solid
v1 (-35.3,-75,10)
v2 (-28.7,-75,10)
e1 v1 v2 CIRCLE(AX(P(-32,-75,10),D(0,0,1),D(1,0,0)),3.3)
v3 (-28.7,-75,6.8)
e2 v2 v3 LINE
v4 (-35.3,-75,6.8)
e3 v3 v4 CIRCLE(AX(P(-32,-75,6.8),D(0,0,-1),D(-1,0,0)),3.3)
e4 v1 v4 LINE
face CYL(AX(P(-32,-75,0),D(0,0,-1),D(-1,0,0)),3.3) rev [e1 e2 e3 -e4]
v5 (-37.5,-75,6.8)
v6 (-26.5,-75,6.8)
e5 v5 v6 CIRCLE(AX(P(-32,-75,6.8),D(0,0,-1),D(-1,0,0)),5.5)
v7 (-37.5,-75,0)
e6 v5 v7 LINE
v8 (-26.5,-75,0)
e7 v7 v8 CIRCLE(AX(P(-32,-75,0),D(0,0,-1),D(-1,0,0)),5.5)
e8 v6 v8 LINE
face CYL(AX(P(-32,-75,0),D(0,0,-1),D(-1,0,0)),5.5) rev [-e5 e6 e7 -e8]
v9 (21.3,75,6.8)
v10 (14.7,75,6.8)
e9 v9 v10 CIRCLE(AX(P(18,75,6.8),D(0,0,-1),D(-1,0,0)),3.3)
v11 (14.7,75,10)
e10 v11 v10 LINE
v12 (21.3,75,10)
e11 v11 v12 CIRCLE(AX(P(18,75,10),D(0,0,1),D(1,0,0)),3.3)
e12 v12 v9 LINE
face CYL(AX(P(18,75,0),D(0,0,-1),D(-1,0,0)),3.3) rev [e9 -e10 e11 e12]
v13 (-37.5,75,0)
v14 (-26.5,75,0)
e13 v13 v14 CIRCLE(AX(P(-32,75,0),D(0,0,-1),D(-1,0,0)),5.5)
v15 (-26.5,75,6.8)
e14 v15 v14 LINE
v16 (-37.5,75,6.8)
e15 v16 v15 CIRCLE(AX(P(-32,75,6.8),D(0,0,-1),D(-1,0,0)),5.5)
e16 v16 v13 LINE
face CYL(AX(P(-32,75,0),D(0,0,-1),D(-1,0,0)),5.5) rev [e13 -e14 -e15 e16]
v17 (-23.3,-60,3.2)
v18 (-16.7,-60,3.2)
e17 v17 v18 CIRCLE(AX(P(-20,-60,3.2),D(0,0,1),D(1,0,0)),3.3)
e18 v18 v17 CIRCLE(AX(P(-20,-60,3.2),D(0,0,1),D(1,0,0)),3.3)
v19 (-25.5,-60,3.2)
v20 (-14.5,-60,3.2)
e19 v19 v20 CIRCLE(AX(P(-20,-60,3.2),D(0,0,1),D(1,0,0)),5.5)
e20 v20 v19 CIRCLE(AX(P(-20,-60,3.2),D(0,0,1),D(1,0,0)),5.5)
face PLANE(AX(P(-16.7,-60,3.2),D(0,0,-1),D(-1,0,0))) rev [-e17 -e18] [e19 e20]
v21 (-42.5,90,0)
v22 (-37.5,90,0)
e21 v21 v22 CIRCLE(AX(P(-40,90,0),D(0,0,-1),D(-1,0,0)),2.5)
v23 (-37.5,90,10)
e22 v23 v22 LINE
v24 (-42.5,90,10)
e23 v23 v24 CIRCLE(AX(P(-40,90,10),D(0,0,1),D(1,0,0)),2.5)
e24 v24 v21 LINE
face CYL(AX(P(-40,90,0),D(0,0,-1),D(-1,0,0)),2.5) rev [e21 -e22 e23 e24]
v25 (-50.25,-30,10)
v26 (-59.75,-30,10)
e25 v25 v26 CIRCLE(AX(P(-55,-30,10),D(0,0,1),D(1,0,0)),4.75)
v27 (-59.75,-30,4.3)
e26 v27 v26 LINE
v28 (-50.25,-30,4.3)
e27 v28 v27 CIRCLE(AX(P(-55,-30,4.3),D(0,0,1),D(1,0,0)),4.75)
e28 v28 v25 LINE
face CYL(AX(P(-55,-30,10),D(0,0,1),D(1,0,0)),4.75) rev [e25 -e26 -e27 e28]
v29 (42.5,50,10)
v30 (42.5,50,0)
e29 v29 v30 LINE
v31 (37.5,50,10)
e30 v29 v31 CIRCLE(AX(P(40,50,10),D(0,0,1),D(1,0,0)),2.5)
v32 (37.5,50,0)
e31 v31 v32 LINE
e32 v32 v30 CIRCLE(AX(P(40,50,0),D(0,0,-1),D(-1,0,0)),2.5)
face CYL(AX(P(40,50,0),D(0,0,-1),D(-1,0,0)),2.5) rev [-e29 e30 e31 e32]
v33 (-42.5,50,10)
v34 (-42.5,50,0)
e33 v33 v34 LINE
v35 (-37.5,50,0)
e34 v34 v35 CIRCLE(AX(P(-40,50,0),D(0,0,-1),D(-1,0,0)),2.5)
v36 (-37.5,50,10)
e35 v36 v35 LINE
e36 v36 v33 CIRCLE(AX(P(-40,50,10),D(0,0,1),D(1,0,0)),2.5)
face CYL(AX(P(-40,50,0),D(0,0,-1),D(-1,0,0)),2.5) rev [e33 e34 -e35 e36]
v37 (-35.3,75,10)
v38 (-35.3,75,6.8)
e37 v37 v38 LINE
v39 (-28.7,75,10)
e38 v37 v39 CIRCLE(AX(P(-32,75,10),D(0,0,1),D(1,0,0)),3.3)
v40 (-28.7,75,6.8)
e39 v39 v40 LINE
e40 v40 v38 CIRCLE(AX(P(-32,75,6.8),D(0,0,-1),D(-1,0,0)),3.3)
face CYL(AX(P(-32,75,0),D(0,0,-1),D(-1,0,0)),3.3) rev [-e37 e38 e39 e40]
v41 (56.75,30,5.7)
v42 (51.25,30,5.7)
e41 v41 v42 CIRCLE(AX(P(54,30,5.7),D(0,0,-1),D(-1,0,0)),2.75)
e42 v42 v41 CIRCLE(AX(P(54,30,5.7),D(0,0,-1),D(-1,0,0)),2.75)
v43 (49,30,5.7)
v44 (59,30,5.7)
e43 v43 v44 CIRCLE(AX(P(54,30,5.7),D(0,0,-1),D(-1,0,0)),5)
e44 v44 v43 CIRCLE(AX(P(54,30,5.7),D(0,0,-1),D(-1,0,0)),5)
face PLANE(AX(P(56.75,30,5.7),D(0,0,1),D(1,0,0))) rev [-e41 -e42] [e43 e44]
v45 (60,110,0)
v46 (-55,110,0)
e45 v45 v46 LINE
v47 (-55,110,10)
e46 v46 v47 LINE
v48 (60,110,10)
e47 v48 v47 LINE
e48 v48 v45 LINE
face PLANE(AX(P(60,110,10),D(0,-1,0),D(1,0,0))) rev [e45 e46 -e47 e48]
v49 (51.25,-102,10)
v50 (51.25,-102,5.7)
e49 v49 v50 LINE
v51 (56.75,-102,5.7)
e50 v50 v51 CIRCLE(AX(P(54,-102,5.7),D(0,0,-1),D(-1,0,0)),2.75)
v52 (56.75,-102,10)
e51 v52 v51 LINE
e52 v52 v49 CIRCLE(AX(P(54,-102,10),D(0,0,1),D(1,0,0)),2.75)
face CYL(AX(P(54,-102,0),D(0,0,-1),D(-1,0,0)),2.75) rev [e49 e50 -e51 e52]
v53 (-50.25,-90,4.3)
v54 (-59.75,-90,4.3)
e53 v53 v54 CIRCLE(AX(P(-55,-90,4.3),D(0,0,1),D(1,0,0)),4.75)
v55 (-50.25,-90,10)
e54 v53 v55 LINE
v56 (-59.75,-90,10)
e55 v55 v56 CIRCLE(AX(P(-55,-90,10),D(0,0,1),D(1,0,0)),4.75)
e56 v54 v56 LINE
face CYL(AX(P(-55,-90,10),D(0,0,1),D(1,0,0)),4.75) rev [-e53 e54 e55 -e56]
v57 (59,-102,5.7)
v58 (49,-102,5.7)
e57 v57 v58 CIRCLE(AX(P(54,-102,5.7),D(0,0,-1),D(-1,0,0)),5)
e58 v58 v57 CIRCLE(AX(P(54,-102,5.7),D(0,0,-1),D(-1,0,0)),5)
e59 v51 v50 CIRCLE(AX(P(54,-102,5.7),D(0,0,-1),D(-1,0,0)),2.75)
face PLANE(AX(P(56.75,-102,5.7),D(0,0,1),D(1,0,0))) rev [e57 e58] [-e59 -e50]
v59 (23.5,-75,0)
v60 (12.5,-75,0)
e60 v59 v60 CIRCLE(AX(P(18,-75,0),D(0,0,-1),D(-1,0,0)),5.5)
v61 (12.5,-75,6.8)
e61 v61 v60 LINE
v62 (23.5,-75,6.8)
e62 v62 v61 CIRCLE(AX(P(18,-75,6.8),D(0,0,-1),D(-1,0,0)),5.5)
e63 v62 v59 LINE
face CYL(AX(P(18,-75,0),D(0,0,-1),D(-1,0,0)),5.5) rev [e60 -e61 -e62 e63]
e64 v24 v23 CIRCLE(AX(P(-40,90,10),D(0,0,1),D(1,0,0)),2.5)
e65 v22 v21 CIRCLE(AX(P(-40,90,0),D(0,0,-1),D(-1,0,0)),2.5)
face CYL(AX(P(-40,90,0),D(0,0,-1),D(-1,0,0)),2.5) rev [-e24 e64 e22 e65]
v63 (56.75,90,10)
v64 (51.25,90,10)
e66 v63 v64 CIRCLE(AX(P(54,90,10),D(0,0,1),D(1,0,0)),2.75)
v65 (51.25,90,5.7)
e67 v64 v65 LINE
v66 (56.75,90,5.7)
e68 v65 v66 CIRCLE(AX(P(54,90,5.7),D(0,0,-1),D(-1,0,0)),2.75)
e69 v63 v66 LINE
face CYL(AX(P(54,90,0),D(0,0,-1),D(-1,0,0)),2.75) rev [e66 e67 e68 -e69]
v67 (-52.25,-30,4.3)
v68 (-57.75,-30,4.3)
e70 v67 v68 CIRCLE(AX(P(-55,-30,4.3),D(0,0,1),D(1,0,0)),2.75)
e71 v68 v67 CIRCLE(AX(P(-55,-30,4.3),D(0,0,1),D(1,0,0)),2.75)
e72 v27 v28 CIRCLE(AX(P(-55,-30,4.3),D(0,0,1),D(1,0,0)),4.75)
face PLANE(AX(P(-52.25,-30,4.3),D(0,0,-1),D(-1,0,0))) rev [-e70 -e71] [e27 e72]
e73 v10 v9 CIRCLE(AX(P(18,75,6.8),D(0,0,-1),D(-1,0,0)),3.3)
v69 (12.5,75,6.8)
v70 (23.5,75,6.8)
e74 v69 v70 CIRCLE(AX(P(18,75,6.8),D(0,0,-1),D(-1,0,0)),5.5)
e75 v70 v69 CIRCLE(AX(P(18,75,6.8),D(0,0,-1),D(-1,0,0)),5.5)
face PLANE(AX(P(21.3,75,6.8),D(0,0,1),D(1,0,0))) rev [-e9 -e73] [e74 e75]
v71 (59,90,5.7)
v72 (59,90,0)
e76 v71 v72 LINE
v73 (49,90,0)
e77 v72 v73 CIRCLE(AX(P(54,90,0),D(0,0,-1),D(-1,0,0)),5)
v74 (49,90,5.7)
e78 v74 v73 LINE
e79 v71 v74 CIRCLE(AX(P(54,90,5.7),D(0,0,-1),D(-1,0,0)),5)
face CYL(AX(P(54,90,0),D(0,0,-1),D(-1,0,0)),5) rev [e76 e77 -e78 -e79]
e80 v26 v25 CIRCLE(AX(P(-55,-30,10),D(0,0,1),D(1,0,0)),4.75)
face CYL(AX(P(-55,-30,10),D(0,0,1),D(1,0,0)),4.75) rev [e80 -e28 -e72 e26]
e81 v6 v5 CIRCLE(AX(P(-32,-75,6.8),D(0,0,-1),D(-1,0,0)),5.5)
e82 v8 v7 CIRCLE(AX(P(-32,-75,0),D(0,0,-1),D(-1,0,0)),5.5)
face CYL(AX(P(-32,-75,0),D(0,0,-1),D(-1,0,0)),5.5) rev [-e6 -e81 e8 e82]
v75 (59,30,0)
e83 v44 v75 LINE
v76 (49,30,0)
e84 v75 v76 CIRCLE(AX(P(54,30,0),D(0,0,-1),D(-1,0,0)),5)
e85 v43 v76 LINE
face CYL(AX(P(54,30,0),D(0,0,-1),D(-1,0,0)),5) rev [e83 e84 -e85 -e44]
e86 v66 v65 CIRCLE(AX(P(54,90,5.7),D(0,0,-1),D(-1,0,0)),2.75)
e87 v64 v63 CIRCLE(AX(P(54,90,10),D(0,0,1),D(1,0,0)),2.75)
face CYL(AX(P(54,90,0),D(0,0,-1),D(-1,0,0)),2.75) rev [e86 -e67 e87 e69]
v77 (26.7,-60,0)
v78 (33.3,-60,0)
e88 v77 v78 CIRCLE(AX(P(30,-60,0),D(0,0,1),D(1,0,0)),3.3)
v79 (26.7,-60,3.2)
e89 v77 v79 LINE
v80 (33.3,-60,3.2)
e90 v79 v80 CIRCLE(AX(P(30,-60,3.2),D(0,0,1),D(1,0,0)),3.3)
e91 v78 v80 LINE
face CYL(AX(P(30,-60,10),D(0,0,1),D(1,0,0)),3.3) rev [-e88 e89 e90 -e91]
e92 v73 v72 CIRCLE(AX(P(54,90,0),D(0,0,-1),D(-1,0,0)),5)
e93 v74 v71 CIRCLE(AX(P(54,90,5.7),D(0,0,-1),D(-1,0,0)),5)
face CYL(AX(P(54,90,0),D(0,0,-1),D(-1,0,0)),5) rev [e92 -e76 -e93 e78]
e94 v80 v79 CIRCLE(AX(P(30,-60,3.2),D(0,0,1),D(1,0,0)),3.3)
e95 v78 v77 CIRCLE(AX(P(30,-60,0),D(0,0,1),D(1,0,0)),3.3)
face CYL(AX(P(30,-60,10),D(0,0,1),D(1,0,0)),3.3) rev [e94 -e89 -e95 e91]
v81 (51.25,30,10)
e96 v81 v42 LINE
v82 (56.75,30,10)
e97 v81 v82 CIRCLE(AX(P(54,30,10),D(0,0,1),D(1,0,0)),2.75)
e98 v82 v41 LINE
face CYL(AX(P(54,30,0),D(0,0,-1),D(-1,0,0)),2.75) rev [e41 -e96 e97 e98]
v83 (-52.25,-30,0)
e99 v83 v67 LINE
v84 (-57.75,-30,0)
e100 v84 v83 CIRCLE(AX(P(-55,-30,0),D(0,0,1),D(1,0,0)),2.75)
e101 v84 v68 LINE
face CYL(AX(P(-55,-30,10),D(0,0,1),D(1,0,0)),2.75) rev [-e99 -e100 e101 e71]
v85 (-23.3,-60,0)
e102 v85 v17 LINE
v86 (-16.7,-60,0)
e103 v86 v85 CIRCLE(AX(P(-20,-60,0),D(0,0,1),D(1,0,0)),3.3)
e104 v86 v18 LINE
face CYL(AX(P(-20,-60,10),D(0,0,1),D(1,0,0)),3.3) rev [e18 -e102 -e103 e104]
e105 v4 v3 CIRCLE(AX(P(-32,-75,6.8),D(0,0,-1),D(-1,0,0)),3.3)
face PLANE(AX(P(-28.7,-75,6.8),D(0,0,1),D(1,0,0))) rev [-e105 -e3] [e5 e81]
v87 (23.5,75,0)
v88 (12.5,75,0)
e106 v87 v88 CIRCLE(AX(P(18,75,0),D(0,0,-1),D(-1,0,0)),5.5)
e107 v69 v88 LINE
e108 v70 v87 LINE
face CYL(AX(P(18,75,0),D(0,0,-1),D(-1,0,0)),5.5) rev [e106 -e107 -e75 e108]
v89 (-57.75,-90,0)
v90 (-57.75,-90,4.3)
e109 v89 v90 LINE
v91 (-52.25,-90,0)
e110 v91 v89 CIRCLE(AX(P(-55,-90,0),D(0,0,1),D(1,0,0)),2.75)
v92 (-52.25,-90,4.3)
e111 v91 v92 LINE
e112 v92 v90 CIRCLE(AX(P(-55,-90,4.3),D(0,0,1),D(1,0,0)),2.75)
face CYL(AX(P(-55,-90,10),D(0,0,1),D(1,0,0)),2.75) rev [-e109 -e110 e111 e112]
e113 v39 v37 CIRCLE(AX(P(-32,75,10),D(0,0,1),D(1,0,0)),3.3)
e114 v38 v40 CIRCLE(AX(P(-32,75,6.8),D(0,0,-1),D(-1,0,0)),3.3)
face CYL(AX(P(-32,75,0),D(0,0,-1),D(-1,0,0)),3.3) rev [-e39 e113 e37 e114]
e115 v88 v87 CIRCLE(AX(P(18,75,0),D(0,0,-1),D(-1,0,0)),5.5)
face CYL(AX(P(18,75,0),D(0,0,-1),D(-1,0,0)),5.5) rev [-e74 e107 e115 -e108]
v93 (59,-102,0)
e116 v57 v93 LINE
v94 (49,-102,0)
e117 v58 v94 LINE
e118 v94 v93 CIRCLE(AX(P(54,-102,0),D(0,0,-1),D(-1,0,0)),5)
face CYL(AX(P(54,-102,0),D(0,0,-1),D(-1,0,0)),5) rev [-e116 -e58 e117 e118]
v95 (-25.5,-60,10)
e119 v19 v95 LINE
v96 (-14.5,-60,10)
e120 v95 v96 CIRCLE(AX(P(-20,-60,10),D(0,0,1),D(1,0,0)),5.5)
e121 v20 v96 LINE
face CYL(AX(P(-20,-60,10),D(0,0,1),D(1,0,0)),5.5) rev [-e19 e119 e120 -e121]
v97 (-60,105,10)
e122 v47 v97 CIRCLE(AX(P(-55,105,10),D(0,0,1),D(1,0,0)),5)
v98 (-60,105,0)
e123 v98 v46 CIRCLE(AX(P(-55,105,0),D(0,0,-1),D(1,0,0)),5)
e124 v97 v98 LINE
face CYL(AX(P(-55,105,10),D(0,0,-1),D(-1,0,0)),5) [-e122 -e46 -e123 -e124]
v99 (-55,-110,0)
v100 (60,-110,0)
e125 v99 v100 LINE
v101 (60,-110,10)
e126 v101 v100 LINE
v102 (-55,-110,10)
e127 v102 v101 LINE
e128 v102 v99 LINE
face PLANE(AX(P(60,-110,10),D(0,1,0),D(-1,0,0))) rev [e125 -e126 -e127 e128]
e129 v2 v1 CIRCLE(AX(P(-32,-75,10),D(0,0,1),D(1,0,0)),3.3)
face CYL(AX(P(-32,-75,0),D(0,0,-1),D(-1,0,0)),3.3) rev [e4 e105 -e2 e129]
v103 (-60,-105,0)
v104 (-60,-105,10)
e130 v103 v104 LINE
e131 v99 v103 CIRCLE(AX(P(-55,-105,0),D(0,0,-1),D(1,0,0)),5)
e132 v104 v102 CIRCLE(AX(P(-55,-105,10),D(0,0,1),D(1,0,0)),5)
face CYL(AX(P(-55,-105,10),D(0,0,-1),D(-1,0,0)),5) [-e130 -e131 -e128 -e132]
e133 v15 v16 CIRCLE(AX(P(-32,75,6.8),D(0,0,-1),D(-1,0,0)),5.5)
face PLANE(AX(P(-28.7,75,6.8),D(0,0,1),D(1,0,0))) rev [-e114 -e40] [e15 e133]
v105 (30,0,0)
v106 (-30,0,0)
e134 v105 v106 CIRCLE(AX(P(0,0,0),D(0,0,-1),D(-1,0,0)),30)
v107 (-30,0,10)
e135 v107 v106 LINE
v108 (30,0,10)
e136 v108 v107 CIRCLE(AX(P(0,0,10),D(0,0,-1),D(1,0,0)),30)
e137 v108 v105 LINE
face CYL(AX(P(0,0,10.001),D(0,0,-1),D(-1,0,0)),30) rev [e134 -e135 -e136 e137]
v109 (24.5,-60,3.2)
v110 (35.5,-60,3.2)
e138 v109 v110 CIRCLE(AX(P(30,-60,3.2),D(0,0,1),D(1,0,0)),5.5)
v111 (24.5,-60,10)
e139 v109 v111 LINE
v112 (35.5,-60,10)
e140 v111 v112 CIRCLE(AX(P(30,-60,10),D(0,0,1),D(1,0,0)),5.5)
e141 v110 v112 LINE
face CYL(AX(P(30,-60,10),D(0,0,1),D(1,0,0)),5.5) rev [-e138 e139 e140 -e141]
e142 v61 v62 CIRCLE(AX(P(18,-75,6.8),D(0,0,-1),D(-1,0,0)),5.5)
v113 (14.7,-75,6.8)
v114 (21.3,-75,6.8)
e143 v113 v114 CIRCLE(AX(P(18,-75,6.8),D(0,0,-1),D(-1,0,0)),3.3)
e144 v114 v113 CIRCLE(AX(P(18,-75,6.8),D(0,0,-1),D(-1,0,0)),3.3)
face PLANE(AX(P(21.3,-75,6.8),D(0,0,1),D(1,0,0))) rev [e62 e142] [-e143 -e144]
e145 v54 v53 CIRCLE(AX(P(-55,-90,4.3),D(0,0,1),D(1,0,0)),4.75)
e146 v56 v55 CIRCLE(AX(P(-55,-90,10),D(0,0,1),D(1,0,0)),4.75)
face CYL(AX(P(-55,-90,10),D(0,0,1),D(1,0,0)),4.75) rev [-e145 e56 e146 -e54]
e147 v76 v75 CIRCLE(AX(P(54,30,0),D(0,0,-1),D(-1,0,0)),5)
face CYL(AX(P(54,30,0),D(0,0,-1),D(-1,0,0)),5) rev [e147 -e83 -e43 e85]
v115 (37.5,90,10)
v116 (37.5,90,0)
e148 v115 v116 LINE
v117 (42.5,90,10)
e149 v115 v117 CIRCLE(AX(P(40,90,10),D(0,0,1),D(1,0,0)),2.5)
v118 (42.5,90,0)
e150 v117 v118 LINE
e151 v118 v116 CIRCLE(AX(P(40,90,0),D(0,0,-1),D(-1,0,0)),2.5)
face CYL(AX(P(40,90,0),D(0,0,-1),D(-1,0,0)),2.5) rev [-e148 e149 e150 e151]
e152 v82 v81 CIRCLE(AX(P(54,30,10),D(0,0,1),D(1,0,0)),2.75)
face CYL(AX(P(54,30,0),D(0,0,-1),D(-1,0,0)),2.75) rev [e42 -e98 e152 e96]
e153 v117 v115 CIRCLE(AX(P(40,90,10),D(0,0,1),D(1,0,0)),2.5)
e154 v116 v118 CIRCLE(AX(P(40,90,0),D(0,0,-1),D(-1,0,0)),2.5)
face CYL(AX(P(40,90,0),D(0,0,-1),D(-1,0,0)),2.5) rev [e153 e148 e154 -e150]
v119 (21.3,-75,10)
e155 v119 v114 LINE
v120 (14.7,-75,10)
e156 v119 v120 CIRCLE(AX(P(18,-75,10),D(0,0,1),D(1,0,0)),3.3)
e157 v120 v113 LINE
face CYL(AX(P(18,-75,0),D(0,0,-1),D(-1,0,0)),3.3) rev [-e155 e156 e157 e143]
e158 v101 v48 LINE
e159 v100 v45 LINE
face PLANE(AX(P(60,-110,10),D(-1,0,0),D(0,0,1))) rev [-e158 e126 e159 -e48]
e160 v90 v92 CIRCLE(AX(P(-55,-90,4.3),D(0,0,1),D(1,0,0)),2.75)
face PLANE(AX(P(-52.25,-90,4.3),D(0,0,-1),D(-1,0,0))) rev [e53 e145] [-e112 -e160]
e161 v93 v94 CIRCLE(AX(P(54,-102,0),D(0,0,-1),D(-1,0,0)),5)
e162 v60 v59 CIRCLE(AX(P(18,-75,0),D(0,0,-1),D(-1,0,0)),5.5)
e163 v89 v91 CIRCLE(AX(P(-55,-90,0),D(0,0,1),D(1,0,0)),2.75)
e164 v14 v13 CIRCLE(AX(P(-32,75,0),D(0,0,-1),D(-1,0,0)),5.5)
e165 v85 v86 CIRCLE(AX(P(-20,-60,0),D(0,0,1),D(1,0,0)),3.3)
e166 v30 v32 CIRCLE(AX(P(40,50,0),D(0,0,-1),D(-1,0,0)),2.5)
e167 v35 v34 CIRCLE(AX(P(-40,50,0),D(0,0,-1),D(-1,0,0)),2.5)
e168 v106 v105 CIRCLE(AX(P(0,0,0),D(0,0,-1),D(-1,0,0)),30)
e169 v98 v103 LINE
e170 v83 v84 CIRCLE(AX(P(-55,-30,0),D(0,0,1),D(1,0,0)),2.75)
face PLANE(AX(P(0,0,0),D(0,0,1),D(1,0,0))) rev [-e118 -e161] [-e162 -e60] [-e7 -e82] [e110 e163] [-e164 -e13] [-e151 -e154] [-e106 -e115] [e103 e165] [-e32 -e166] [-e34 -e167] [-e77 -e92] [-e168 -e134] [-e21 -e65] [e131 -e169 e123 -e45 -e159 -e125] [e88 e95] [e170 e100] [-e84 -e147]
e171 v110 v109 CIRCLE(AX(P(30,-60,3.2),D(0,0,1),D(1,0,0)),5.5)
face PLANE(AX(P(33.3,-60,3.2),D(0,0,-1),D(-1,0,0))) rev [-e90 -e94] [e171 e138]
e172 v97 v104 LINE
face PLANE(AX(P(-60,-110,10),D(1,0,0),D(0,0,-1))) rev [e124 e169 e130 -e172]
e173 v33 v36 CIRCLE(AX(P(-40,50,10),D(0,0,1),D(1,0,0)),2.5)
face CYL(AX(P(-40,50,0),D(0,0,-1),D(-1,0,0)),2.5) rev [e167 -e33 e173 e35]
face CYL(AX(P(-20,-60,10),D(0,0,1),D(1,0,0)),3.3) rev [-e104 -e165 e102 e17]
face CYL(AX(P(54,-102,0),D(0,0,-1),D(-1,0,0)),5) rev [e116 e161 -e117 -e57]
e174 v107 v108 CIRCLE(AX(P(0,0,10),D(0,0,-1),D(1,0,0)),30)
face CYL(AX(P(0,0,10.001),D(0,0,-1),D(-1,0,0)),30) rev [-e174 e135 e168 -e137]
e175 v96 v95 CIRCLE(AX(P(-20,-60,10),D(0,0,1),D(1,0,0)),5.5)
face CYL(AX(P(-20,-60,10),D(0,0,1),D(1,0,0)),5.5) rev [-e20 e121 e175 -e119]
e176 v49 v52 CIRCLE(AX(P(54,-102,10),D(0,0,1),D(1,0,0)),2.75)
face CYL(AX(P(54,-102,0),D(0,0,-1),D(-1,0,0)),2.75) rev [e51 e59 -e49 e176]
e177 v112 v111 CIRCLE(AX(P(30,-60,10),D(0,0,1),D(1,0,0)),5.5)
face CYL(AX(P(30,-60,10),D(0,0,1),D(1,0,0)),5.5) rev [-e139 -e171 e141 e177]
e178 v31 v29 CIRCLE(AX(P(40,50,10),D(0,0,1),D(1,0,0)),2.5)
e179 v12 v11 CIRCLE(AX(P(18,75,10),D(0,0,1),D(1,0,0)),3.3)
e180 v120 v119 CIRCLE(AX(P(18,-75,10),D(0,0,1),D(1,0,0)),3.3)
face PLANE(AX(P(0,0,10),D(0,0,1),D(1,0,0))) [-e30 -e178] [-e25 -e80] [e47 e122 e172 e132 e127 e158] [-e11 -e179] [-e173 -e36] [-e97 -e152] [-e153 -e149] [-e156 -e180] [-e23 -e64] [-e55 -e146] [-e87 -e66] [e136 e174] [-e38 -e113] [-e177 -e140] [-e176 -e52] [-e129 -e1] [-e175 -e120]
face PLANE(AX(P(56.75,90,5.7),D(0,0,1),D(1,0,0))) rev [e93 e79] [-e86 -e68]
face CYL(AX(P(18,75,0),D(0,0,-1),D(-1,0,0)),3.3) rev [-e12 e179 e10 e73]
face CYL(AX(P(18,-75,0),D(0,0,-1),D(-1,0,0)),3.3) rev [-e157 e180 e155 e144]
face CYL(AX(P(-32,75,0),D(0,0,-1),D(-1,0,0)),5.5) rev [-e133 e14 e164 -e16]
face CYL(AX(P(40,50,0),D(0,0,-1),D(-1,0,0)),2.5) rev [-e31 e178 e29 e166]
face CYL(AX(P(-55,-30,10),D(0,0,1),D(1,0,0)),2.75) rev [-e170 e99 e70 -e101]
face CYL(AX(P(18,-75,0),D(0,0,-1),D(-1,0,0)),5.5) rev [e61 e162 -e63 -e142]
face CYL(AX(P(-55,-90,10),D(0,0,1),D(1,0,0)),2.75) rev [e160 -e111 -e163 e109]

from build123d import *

# Parameters (mm, degrees)
SKETCH_1_W                = 120
SKETCH_1_H                = 220
EXTRUDE_1_DEPTH           = 10
HOLE_WIZARD_M6_1_D        = 5
HOLE_WIZARD_1_D           = 6.6
HOLE_WIZARD_1_CBORE_D     = 11
HOLE_WIZARD_1_CBORE_DEPTH = 6.8
CUT_EXTRUDE_1_REACH       = 127.698
SKETCH_6_R                = 30
HOLE_WIZARD_2_D           = 5.5
HOLE_WIZARD_2_CBORE_D     = 9.5
HOLE_WIZARD_2_CBORE_DEPTH = 5.7
HOLE_WIZARD_3_D           = 6.6
HOLE_WIZARD_3_CBORE_D     = 11
HOLE_WIZARD_3_CBORE_DEPTH = 6.8
HOLE_WIZARD_4_D           = 5.5
HOLE_WIZARD_4_CBORE_D     = 10
HOLE_WIZARD_4_CBORE_DEPTH = 5.7
FILLET_1_R                = 5


with BuildPart() as part:
    # 草图1 → 凸台-拉伸1 (new body)
    with BuildSketch(Plane.XY):
        Rectangle(SKETCH_1_W, SKETCH_1_H)
    extrude(amount=EXTRUDE_1_DEPTH)

    # M6 螺纹孔1 (through all)
    with Locations(Plane(origin=(0, 0, 0), x_dir=(-1, 0, 0), z_dir=(0, 0, -1))):
        with Locations((-40, 90), (-40, 50), (40, 90), (40, 50)):
            Hole(HOLE_WIZARD_M6_1_D / 2)

    # 打孔尺寸(%根据)内六角圆柱头螺钉的类型1 (through all)
    with Locations(Plane(origin=(0, 0, 0), x_dir=(-1, 0, 0), z_dir=(0, 0, -1))):
        with Locations((32, -75), (-18, -75), (32, 75), (-18, 75)):
            CounterBoreHole(HOLE_WIZARD_1_D / 2, HOLE_WIZARD_1_CBORE_D / 2, HOLE_WIZARD_1_CBORE_DEPTH)

    # 草图6 → 切除-拉伸1 (cut, up to next)
    with BuildSketch(Plane(origin=(0, 0, 0), x_dir=(-1, 0, 0), z_dir=(0, 0, -1)), mode=Mode.PRIVATE) as cut_extrude_1_sk1:
        Circle(SKETCH_6_R)
    cut_extrude_1_tool1 = extrude(cut_extrude_1_sk1.sketch, amount=-CUT_EXTRUDE_1_REACH, mode=Mode.PRIVATE) & part.part
    add(cut_extrude_1_tool1.solids().sort_by_distance((0, 0, 0))[0], mode=Mode.SUBTRACT)

    # 打孔尺寸(%根据)内六角圆柱头螺钉的类型2 (through all)
    with Locations(Plane.XY.offset(10)):
        with Locations((-55, -30), (-55, -90)):
            CounterBoreHole(HOLE_WIZARD_2_D / 2, HOLE_WIZARD_2_CBORE_D / 2, HOLE_WIZARD_2_CBORE_DEPTH)

    # 打孔尺寸(%根据)内六角圆柱头螺钉的类型3 (through all)
    with Locations(Plane.XY.offset(10)):
        with Locations((-20, -60), (30, -60)):
            CounterBoreHole(HOLE_WIZARD_3_D / 2, HOLE_WIZARD_3_CBORE_D / 2, HOLE_WIZARD_3_CBORE_DEPTH)

    # 打孔尺寸(%根据)内六角圆柱头螺钉的类型4 (through all)
    with Locations(Plane(origin=(0, 0, 0), x_dir=(-1, 0, 0), z_dir=(0, 0, -1))):
        with Locations((-54, 30), (-54, 90), (-54, -102)):
            CounterBoreHole(HOLE_WIZARD_4_D / 2, HOLE_WIZARD_4_CBORE_D / 2, HOLE_WIZARD_4_CBORE_DEPTH)

    # 圆角1
    fillet_1_edges = [part.edges().sort_by_distance(p)[0] for p in [
        (-60, 110, 5),
        (-60, -110, 5),
    ]]
    fillet(fillet_1_edges, radius=FILLET_1_R)


solid = part.part
